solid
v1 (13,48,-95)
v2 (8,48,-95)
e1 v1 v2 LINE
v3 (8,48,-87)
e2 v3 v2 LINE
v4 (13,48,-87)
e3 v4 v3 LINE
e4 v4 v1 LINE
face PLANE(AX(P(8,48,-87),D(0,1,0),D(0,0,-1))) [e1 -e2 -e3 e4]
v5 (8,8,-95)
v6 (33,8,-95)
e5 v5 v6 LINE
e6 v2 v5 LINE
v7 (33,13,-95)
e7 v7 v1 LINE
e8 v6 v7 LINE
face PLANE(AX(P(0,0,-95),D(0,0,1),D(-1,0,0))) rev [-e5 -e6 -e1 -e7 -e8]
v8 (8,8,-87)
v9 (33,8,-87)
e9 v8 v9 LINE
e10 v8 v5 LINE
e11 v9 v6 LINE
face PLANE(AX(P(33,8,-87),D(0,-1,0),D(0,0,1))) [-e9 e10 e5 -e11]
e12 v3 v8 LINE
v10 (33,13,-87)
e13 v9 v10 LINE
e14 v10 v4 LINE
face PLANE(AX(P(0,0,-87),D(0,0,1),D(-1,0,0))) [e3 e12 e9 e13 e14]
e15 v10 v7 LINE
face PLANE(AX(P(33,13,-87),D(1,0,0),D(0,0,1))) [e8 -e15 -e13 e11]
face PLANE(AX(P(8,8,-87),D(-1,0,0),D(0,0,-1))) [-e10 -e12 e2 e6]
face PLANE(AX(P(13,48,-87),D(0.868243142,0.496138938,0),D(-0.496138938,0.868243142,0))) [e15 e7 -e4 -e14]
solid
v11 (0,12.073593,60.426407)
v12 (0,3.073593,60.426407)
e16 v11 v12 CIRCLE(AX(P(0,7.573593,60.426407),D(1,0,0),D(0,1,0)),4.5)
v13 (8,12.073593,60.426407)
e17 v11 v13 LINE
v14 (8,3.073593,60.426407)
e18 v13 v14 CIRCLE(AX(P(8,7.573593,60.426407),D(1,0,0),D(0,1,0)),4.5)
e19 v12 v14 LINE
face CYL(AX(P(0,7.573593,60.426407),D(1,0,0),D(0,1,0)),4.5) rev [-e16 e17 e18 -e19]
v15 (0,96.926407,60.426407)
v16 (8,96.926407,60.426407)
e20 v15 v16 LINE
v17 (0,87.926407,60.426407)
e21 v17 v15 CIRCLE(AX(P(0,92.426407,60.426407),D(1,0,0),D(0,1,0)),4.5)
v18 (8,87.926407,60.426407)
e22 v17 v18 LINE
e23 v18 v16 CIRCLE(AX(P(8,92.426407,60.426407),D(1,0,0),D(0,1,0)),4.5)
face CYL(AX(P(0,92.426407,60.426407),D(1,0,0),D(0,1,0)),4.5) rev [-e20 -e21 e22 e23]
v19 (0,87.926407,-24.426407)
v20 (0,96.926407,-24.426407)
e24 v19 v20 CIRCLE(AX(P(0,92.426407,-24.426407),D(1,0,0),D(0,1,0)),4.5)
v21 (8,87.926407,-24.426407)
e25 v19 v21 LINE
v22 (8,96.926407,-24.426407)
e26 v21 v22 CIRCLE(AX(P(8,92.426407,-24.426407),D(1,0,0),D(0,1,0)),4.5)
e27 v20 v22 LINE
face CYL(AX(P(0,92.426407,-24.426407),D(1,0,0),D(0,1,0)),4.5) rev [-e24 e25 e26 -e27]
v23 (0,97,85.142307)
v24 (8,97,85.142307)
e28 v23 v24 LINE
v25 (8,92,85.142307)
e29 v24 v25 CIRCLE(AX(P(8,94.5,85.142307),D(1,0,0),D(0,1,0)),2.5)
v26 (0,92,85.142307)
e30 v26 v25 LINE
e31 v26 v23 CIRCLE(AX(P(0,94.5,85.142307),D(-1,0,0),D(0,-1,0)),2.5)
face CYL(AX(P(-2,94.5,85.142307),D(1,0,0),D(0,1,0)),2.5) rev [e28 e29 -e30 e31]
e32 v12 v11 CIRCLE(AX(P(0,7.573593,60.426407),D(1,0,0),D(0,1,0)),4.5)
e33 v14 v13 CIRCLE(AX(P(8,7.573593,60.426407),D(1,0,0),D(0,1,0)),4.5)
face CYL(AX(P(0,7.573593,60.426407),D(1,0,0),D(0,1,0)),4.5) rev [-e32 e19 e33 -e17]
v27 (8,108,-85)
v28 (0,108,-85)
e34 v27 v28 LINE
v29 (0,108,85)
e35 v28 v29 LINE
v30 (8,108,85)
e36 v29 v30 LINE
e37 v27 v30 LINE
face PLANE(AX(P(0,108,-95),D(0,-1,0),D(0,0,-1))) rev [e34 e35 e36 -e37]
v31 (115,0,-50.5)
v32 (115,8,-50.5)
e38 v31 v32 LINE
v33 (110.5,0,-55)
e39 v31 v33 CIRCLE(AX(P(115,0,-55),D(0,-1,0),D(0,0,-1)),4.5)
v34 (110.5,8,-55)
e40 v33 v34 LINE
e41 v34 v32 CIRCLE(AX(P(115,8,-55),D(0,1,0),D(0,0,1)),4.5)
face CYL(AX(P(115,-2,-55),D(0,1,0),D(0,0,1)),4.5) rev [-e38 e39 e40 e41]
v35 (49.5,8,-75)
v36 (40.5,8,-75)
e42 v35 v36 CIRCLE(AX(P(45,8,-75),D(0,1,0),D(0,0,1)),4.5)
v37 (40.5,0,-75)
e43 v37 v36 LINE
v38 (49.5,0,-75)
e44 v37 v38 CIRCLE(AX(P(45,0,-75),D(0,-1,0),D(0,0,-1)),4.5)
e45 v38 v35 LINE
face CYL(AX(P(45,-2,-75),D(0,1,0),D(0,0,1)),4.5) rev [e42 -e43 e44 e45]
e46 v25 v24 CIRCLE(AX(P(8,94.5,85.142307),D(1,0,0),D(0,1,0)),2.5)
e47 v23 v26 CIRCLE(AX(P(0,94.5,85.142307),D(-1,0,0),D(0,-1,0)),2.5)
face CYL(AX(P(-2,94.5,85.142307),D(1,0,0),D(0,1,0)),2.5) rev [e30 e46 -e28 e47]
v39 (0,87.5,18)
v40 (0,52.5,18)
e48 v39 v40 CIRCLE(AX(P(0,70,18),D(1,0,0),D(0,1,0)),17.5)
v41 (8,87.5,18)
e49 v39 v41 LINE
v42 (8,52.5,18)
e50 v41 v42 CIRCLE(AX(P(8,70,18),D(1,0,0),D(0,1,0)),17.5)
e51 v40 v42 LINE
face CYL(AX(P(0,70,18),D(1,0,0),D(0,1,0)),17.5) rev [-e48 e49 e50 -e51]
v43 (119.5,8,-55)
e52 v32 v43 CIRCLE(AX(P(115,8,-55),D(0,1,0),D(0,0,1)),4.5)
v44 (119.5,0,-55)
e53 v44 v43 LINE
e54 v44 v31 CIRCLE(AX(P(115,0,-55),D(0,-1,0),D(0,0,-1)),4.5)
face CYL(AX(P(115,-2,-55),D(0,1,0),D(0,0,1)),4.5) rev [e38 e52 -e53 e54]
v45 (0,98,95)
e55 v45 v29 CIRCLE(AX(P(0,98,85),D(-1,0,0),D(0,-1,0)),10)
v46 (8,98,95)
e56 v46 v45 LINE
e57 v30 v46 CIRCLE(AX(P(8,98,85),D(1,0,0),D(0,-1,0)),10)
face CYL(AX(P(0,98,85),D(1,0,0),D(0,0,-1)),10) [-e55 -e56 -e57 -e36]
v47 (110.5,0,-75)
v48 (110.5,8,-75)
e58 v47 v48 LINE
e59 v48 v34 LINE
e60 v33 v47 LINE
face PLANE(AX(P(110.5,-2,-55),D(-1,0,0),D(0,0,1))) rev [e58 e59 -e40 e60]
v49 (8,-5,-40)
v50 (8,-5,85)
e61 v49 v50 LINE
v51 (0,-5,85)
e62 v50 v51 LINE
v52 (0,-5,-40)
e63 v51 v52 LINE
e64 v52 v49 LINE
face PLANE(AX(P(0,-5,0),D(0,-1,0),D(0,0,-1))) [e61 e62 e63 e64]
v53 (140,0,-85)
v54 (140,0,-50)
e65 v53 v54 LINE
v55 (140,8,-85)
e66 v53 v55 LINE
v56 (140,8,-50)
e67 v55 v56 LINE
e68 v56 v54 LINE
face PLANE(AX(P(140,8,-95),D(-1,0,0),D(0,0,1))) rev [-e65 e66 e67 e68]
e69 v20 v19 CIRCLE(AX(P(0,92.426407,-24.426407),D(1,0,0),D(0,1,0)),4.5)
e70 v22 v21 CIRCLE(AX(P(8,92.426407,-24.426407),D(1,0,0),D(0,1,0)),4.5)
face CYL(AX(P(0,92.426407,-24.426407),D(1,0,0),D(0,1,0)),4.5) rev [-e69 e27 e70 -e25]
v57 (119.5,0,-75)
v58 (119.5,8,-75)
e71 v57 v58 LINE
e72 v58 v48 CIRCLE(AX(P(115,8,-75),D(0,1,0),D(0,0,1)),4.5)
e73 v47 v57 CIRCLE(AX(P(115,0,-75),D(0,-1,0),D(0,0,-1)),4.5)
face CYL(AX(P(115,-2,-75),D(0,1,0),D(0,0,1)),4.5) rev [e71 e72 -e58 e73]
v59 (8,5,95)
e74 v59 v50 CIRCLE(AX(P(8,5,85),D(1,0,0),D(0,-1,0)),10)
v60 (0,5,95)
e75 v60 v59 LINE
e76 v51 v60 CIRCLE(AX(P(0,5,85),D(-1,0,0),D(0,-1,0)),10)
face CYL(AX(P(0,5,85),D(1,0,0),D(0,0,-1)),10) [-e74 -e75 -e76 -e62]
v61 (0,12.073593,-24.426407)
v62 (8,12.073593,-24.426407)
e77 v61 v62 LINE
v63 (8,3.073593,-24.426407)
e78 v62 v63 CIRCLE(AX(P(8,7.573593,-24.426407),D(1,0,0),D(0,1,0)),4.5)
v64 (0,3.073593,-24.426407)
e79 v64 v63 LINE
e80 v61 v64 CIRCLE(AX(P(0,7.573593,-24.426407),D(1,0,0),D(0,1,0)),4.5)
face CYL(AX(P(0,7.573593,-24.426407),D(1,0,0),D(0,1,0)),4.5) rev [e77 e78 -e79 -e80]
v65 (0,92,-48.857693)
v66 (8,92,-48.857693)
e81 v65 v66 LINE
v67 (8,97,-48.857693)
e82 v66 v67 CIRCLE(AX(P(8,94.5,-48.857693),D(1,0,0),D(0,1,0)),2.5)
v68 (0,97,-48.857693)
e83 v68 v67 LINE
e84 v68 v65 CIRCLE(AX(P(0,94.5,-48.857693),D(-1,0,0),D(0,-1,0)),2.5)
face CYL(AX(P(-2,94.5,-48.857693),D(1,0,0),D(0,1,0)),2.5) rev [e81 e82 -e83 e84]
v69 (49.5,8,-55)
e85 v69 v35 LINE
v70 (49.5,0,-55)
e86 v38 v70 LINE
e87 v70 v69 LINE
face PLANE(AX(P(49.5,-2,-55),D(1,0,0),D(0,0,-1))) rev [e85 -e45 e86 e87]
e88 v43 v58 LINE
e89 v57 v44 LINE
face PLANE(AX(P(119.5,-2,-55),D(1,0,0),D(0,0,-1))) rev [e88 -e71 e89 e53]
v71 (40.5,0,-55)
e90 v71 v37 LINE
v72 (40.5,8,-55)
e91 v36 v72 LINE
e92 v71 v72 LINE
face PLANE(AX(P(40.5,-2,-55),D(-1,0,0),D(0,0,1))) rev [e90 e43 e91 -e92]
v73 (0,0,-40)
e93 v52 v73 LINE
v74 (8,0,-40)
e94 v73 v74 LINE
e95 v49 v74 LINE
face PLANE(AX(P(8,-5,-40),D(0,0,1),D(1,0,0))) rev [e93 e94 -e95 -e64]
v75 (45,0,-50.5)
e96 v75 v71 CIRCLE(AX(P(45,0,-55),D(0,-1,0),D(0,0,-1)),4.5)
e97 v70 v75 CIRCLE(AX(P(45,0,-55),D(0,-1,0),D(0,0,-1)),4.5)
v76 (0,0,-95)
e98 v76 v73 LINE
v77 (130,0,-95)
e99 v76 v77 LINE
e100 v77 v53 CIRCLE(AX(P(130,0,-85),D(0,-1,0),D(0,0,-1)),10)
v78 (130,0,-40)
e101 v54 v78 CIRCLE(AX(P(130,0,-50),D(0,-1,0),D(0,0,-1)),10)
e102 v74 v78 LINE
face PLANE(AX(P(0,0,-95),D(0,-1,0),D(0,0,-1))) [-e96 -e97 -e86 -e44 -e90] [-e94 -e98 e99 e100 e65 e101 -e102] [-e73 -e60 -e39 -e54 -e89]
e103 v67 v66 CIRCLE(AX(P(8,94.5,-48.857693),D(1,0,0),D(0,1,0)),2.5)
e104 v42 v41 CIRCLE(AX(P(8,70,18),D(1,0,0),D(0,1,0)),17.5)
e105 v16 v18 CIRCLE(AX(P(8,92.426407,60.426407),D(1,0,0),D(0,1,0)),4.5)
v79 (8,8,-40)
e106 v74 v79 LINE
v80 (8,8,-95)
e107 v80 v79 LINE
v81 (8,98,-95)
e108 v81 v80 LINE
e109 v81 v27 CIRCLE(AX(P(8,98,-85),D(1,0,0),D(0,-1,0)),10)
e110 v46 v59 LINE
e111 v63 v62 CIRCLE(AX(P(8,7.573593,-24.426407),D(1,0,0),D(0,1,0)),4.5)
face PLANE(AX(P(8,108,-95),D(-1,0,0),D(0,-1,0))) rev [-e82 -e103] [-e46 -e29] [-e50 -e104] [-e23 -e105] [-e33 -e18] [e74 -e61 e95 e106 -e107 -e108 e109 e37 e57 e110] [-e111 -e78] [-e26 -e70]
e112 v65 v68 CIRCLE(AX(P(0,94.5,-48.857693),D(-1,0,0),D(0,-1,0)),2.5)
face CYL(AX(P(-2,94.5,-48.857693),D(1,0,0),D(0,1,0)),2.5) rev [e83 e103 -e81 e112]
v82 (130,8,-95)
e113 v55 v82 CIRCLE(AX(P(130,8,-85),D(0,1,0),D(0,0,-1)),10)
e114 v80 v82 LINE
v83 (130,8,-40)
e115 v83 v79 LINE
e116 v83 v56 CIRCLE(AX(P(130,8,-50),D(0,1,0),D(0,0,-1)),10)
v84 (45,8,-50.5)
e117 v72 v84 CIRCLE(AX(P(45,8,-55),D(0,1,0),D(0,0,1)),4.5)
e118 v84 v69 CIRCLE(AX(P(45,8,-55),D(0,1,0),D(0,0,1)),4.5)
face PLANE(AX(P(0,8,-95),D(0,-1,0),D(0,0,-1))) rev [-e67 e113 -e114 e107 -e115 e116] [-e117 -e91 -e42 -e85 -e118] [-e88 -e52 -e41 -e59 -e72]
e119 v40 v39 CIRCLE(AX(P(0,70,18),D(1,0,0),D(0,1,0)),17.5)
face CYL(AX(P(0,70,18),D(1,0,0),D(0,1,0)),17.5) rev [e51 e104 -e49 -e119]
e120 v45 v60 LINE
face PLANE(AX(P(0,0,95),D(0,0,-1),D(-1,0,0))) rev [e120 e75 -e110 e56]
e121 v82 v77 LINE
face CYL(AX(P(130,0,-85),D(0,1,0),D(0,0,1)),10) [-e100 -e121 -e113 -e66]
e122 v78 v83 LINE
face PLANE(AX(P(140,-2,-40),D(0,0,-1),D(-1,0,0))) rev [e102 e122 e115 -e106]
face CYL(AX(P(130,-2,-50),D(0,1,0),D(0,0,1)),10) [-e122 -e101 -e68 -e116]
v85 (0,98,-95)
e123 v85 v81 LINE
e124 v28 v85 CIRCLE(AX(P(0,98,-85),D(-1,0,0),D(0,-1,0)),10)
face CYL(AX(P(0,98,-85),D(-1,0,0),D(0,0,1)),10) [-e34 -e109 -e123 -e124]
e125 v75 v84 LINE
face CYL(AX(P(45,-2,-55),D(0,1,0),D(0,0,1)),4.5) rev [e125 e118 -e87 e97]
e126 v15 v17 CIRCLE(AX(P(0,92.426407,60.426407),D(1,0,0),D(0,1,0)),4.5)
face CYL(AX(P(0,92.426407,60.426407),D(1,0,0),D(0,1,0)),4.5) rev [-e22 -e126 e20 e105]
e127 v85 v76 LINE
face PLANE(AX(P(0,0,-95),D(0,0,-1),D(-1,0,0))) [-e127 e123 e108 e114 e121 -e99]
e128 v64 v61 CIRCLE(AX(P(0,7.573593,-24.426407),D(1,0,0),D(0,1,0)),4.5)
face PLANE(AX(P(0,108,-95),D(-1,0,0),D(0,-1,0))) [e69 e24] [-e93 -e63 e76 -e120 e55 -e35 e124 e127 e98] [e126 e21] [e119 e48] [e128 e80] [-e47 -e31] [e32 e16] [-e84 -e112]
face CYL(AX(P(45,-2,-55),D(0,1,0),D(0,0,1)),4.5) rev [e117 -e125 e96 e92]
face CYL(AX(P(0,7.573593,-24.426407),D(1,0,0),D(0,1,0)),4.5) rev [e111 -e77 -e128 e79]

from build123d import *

# Parameters (mm, degrees)
EXTRUDE_1_DEPTH     = 95
SKETCH_2_R          = 4.5
CUT_EXTRUDE_1_DEPTH = 10
EXTRUDE_1_2_DEPTH   = 8
SKETCH_5_R          = 4.5
SKETCH_5_R_2        = 17.5
CUT_EXTRUDE_2_DEPTH = 196.225510628
FILLET_1_R          = 10
CUT_EXTRUDE_4_DEPTH = 10
SKETCH_8_W          = 132
SKETCH_8_H          = 163.82032184
CUT_EXTRUDE_5_DEPTH = 10
FILLET_2_R          = 10
SKETCH_9_W          = 8
SKETCH_9_H          = 135
EXTRUDE_2_DEPTH     = 5
FILLET_3_R          = 10
SKETCH_10_R         = 2.5
CUT_EXTRUDE_6_DEPTH = 10


with BuildPart() as part:
    # 草图1 → Extrude 1 (new, symmetric)
    with BuildSketch(Plane.XY):
        Polygon((0, 108), (0, 0), (140, 0), (140, 8), (8, 8), (8, 108), align=None)
    extrude(amount=EXTRUDE_1_DEPTH, both=True)

    # 草图2 → 切除-拉伸1 (cut)
    with BuildSketch(Plane(origin=(0, 8, 0), x_dir=(1, 0, 0), z_dir=(0, 1, 0))):
        with Locations(Location((115, 65, 0), (0, 0, 270))):
            Circle(SKETCH_2_R)
        with Locations(Location((45, 65, 0), (0, 0, 270))):
            Circle(SKETCH_2_R)
        with Locations(Location((115, -65, 0), (0, 0, 270))):
            Circle(SKETCH_2_R)
        with Locations(Location((45, -65, 0), (0, 0, 270))):
            Circle(SKETCH_2_R)
    extrude(amount=-CUT_EXTRUDE_1_DEPTH, mode=Mode.SUBTRACT)

    # 草图5 → 切除-拉伸2 (cut, through all)
    with BuildSketch(Plane(origin=(8, 0, 0), x_dir=(0, 0, -1), z_dir=(1, 0, 0))):
        with Locations(Location((-60.426406871, 92.426406871, 0), (0, 0, 90))):
            Circle(SKETCH_5_R)
        with Locations(Location((-60.426406871, 7.573593129, 0), (0, 0, 90))):
            Circle(SKETCH_5_R)
        with Locations(Location((24.426406871, 7.573593129, 0), (0, 0, 90))):
            Circle(SKETCH_5_R)
        with Locations(Location((24.426406871, 92.426406871, 0), (0, 0, 90))):
            Circle(SKETCH_5_R)
        with Locations(Location((-18, 70, 0), (0, 0, 90))):
            Circle(SKETCH_5_R_2)
    extrude(amount=-CUT_EXTRUDE_2_DEPTH, mode=Mode.SUBTRACT)

    # 圆角1
    fillet_1_edges = [part.edges().sort_by_distance(p)[0] for p in [
        (4, 108, -95),
        (4, 108, 95),
        (140, 4, 95),
        (140, 4, -95),
    ]]
    fillet(fillet_1_edges, radius=FILLET_1_R)

    # 草图7 → 切除-拉伸4 (cut)
    with BuildSketch(Plane(origin=(0, 8, 0), x_dir=(1, 0, 0), z_dir=(0, 1, 0))):
        with BuildLine():
            Line((40.5, 55), (40.5, 75))
            ThreePointArc((40.5, 75), (45, 79.5), (49.5, 75))
            Line((49.5, 75), (49.5, 55))
            ThreePointArc((49.5, 55), (45, 50.5), (40.5, 55))
        make_face()
        with BuildLine():
            Line((110.5, 55), (110.5, 75))
            ThreePointArc((110.5, 75), (115, 79.5), (119.5, 75))
            Line((119.5, 75), (119.5, 55))
            ThreePointArc((119.5, 55), (115, 50.5), (110.5, 55))
        make_face()
        with BuildLine():
            Line((110.5, -75), (110.5, -55))
            ThreePointArc((110.5, -55), (115, -50.5), (119.5, -55))
            Line((119.5, -55), (119.5, -75))
            ThreePointArc((119.5, -75), (115, -79.5), (110.5, -75))
        make_face()
        with BuildLine():
            Line((40.5, -75), (40.5, -55))
            ThreePointArc((40.5, -55), (45, -50.5), (49.5, -55))
            Line((49.5, -55), (49.5, -75))
            ThreePointArc((49.5, -75), (45, -79.5), (40.5, -75))
        make_face()
    extrude(amount=-CUT_EXTRUDE_4_DEPTH, mode=Mode.SUBTRACT)

    # 草图8 → 切除-拉伸5 (cut)
    with BuildSketch(Plane(origin=(0, 8, 0), x_dir=(1, 0, 0), z_dir=(0, 1, 0))):
        with Locations((74, -41.91016092)):
            Rectangle(SKETCH_8_W, SKETCH_8_H)
    extrude(amount=-CUT_EXTRUDE_5_DEPTH, mode=Mode.SUBTRACT)

    # 圆角2
    fillet_2_edges = [part.edges().sort_by_distance(p)[0] for p in [
        (140, 4, -40),
    ]]
    fillet(fillet_2_edges, radius=FILLET_2_R)

    # 草图9 → 凸台-拉伸2 (add)
    with BuildSketch(Plane.XZ):
        with Locations((4, 27.5)):
            Rectangle(SKETCH_9_W, SKETCH_9_H)
    extrude(amount=EXTRUDE_2_DEPTH)

    # 圆角3
    fillet_3_edges = [part.edges().sort_by_distance(p)[0] for p in [
        (4, -5, 95),
    ]]
    fillet(fillet_3_edges, radius=FILLET_3_R)

    # 草图10 → 切除-拉伸6 (cut)
    with BuildSketch(Plane(origin=(8, 0, 0), x_dir=(0, 0, -1), z_dir=(1, 0, 0))):
        with Locations(Location((-85.142306872, 94.5, 0), (0, 0, 90))):
            Circle(SKETCH_10_R)
        with Locations(Location((48.857693128, 94.5, 0), (0, 0, 90))):
            Circle(SKETCH_10_R)
    extrude(amount=-CUT_EXTRUDE_6_DEPTH, mode=Mode.SUBTRACT)


with BuildPart() as body_2:
    # 草图4 → Extrude 1 2 (new body)
    with BuildSketch(Plane.XY.offset(95)):
        Polygon((8, 48), (13, 48), (33, 13), (33, 8), (8, 8), align=None)
    extrude(amount=-EXTRUDE_1_2_DEPTH)


with BuildPart() as body_3:
    # 镜向2: mirrored copy
    add(body_2.part.mirror(Plane.XY))


solid = Compound([part.part, body_3.part])
